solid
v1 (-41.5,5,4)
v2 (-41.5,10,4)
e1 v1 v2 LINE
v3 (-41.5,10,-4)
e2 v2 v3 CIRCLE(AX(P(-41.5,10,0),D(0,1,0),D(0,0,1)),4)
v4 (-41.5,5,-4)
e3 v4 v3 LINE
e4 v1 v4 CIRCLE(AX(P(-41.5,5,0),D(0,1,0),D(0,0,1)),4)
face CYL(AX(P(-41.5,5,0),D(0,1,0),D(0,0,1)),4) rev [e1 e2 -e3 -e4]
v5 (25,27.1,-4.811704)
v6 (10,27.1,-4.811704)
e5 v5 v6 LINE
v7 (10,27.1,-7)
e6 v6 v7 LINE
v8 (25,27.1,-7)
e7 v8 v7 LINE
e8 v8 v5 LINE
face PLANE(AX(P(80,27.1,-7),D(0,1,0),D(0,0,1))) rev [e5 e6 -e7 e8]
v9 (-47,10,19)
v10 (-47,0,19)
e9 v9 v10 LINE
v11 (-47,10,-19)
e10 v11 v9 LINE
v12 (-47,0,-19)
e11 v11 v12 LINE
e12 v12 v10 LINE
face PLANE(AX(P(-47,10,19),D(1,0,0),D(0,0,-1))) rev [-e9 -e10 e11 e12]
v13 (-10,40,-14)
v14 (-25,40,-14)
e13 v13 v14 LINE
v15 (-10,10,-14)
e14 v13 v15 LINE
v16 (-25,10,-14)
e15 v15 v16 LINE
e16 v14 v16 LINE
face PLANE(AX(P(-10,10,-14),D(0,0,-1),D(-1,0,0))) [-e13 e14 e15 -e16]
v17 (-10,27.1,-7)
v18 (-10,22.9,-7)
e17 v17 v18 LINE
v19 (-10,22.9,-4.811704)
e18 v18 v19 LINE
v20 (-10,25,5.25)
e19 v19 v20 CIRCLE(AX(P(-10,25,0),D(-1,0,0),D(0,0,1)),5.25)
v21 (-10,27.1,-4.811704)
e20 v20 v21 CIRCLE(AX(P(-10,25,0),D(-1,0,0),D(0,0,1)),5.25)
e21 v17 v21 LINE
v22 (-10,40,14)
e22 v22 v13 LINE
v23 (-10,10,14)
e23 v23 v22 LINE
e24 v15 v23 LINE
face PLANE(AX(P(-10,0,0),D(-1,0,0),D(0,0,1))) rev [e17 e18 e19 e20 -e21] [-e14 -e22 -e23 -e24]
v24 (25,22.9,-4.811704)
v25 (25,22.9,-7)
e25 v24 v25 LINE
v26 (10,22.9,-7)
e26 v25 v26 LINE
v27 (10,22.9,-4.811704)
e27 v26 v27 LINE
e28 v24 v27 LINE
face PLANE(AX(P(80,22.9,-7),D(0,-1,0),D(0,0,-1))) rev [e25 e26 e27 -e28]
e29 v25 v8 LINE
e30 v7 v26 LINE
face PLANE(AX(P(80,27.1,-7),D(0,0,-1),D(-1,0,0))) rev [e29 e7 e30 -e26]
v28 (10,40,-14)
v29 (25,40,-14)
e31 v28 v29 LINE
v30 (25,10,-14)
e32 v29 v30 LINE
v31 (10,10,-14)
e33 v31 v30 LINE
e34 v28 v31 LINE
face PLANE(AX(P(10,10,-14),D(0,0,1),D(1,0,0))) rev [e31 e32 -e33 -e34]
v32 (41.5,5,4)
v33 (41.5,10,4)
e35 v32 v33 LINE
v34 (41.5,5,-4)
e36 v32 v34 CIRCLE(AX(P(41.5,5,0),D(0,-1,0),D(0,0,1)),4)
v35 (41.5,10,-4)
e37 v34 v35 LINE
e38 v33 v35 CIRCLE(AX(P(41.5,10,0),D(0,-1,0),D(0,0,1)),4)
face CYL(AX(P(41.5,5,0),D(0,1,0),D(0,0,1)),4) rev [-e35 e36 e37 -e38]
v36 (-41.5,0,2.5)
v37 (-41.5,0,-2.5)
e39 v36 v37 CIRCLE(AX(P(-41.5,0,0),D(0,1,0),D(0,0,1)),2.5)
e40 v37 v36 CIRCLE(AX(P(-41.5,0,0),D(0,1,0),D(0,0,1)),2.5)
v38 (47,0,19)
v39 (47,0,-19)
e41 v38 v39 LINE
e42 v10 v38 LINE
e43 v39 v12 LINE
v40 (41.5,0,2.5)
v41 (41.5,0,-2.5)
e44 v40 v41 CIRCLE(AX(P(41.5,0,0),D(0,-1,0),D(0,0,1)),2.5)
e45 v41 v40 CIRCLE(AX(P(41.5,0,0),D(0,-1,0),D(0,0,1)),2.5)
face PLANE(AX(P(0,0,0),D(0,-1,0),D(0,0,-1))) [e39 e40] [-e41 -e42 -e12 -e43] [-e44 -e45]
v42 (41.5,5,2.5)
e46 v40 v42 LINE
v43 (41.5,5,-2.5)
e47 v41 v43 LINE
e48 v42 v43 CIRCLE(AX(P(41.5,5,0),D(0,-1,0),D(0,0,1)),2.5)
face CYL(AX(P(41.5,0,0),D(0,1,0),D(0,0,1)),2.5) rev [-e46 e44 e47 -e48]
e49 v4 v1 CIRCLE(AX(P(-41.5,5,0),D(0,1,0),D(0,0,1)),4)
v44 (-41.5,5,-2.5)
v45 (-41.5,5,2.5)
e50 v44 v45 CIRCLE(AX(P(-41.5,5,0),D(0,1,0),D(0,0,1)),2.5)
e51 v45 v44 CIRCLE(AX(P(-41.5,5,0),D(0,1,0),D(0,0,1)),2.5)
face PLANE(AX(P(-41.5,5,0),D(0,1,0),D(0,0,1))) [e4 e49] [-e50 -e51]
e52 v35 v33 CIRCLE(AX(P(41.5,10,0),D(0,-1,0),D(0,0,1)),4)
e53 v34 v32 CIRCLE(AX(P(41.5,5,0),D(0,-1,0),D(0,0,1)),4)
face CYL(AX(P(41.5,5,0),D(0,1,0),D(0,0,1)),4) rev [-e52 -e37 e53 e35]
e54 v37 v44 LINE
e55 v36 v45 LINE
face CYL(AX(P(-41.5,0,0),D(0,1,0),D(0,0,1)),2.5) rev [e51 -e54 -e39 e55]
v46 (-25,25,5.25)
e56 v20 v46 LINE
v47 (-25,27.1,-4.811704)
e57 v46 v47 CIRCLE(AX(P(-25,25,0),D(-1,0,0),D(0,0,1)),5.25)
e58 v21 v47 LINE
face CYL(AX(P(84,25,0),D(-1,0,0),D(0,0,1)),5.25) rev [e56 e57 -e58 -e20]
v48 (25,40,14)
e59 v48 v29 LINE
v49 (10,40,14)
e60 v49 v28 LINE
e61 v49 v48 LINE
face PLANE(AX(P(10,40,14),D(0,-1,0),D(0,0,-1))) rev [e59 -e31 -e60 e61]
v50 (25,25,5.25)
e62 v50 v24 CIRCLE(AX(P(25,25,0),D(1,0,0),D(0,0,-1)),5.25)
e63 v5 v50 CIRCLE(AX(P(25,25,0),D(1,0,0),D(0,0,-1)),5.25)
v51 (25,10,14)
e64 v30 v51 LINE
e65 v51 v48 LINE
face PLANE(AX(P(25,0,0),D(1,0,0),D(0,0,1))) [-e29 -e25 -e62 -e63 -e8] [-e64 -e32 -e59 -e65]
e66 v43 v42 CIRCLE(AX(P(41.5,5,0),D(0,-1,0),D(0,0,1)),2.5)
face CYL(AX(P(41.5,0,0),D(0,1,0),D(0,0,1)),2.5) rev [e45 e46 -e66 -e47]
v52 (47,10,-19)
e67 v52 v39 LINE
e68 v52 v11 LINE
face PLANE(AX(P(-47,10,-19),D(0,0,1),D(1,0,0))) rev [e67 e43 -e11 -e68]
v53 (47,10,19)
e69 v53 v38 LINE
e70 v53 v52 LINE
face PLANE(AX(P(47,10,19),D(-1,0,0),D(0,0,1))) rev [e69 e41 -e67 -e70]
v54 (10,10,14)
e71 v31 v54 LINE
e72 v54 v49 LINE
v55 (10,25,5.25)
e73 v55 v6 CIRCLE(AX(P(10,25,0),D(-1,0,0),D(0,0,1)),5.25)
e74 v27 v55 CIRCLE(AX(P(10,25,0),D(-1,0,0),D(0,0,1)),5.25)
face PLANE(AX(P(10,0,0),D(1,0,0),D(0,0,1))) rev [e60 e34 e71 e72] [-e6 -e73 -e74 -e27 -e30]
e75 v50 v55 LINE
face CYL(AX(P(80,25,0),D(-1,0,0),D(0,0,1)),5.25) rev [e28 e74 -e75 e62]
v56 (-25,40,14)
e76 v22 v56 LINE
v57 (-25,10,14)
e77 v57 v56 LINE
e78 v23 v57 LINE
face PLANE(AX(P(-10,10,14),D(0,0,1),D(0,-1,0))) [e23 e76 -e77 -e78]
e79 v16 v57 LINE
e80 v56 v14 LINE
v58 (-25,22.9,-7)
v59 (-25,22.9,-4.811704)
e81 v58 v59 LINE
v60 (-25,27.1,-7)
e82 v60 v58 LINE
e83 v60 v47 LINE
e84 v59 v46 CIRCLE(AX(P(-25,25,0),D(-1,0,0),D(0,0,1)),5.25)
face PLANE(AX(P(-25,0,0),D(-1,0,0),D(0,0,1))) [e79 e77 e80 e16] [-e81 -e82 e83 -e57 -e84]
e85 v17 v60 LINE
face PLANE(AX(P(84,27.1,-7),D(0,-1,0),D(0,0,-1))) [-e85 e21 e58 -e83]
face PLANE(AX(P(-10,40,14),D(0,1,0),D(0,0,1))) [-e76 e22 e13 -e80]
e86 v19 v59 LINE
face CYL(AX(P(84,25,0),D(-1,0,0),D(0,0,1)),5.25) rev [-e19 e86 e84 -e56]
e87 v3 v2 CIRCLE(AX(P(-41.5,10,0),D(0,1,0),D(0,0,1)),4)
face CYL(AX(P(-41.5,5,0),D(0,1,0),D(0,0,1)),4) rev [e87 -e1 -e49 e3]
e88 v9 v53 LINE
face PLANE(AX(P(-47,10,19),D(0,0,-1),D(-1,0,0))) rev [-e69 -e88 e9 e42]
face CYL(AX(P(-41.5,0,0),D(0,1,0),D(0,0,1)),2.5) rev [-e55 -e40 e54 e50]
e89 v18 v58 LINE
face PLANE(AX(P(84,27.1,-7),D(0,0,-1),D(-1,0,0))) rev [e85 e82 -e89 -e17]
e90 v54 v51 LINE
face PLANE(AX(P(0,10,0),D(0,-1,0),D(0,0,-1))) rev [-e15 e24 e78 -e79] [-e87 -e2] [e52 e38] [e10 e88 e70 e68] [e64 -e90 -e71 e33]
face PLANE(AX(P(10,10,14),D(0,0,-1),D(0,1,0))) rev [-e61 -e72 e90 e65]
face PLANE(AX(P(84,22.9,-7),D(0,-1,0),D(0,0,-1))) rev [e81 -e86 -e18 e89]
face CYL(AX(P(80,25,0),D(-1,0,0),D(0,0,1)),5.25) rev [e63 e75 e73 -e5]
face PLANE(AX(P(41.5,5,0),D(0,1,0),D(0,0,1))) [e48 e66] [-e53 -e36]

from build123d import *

# Parameters (mm, degrees)
SKETCH1_W           = 94
SKETCH1_H           = 38
BOSS_EXTRUDE1_DEPTH = 10
SKETCH2_R           = 4
CUT_EXTRUDE1_DEPTH  = 5
SKETCH3_R           = 2.5
CUT_EXTRUDE2_DEPTH  = 5
SKETCH4_W           = 28
SKETCH4_H           = 30
BOSS_EXTRUDE2_DEPTH = 15
CUT_EXTRUDE3_DEPTH  = 109
CUT_EXTRUDE4_DEPTH  = 70


with BuildPart() as part:
    # Sketch1 → Boss-Extrude1 (new body)
    with BuildSketch(Plane(origin=(0, 0, 0), x_dir=(1, 0, 0), z_dir=(0, 1, 0))):
        Rectangle(SKETCH1_W, SKETCH1_H)
    extrude(amount=BOSS_EXTRUDE1_DEPTH)

    # Sketch2 → Cut-Extrude1 (cut)
    with BuildSketch(Plane(origin=(0, 10, 0), x_dir=(1, 0, 0), z_dir=(0, 1, 0))):
        with Locations(Location((-41.5, 0, 0), (0, 0, 270))):
            Circle(SKETCH2_R)
    cut_extrude1 = extrude(amount=-CUT_EXTRUDE1_DEPTH, mode=Mode.SUBTRACT)

    # Sketch3 → Cut-Extrude2 (cut)
    with BuildSketch(Plane(origin=(0, 5, 0), x_dir=(1, 0, 0), z_dir=(0, 1, 0))):
        with Locations(Location((-41.5, 0, 0), (0, 0, 270))):
            Circle(SKETCH3_R)
    cut_extrude2 = extrude(amount=-CUT_EXTRUDE2_DEPTH, mode=Mode.SUBTRACT)

    # Sketch4 → Boss-Extrude2 (add)
    with BuildSketch(Plane.ZY.offset(25)):
        with Locations((0, 25)):
            Rectangle(SKETCH4_W, SKETCH4_H)
    boss_extrude2 = extrude(amount=-BOSS_EXTRUDE2_DEPTH)

    # Sketch6 → Cut-Extrude3 (cut)
    with BuildSketch(Plane.ZY.offset(25)):
        with BuildLine():
            Line((-7, 27.1), (-4.81170448, 27.1))
            ThreePointArc((-4.81170448, 27.1), (5.25, 25), (-4.81170448, 22.9))
            Line((-4.81170448, 22.9), (-7, 22.9))
            Line((-7, 22.9), (-7, 27.1))
        make_face()
    extrude(amount=-CUT_EXTRUDE3_DEPTH, mode=Mode.SUBTRACT)

    # Mirror1: Cut-Extrude1, Cut-Extrude2, Boss-Extrude2 across plane
    add(cut_extrude1.mirror(Plane(origin=(0, 0, 0), x_dir=(0, 0, 1), z_dir=(1, 0, 0))), mode=Mode.SUBTRACT)
    add(cut_extrude2.mirror(Plane(origin=(0, 0, 0), x_dir=(0, 0, 1), z_dir=(1, 0, 0))), mode=Mode.SUBTRACT)
    add(boss_extrude2.mirror(Plane(origin=(0, 0, 0), x_dir=(0, 0, 1), z_dir=(1, 0, 0))))

    # Sketch7 → Cut-Extrude4 (cut)
    with BuildSketch(Plane.ZY.offset(-10)):
        with BuildLine():
            Line((-7, 22.9), (-4.81170448, 22.9))
            ThreePointArc((-4.81170448, 22.9), (5.25, 25), (-4.81170448, 27.1))
            Line((-4.81170448, 27.1), (-7, 27.1))
            Line((-7, 27.1), (-7, 22.9))
        make_face()
    extrude(amount=-CUT_EXTRUDE4_DEPTH, mode=Mode.SUBTRACT)


solid = part.part
